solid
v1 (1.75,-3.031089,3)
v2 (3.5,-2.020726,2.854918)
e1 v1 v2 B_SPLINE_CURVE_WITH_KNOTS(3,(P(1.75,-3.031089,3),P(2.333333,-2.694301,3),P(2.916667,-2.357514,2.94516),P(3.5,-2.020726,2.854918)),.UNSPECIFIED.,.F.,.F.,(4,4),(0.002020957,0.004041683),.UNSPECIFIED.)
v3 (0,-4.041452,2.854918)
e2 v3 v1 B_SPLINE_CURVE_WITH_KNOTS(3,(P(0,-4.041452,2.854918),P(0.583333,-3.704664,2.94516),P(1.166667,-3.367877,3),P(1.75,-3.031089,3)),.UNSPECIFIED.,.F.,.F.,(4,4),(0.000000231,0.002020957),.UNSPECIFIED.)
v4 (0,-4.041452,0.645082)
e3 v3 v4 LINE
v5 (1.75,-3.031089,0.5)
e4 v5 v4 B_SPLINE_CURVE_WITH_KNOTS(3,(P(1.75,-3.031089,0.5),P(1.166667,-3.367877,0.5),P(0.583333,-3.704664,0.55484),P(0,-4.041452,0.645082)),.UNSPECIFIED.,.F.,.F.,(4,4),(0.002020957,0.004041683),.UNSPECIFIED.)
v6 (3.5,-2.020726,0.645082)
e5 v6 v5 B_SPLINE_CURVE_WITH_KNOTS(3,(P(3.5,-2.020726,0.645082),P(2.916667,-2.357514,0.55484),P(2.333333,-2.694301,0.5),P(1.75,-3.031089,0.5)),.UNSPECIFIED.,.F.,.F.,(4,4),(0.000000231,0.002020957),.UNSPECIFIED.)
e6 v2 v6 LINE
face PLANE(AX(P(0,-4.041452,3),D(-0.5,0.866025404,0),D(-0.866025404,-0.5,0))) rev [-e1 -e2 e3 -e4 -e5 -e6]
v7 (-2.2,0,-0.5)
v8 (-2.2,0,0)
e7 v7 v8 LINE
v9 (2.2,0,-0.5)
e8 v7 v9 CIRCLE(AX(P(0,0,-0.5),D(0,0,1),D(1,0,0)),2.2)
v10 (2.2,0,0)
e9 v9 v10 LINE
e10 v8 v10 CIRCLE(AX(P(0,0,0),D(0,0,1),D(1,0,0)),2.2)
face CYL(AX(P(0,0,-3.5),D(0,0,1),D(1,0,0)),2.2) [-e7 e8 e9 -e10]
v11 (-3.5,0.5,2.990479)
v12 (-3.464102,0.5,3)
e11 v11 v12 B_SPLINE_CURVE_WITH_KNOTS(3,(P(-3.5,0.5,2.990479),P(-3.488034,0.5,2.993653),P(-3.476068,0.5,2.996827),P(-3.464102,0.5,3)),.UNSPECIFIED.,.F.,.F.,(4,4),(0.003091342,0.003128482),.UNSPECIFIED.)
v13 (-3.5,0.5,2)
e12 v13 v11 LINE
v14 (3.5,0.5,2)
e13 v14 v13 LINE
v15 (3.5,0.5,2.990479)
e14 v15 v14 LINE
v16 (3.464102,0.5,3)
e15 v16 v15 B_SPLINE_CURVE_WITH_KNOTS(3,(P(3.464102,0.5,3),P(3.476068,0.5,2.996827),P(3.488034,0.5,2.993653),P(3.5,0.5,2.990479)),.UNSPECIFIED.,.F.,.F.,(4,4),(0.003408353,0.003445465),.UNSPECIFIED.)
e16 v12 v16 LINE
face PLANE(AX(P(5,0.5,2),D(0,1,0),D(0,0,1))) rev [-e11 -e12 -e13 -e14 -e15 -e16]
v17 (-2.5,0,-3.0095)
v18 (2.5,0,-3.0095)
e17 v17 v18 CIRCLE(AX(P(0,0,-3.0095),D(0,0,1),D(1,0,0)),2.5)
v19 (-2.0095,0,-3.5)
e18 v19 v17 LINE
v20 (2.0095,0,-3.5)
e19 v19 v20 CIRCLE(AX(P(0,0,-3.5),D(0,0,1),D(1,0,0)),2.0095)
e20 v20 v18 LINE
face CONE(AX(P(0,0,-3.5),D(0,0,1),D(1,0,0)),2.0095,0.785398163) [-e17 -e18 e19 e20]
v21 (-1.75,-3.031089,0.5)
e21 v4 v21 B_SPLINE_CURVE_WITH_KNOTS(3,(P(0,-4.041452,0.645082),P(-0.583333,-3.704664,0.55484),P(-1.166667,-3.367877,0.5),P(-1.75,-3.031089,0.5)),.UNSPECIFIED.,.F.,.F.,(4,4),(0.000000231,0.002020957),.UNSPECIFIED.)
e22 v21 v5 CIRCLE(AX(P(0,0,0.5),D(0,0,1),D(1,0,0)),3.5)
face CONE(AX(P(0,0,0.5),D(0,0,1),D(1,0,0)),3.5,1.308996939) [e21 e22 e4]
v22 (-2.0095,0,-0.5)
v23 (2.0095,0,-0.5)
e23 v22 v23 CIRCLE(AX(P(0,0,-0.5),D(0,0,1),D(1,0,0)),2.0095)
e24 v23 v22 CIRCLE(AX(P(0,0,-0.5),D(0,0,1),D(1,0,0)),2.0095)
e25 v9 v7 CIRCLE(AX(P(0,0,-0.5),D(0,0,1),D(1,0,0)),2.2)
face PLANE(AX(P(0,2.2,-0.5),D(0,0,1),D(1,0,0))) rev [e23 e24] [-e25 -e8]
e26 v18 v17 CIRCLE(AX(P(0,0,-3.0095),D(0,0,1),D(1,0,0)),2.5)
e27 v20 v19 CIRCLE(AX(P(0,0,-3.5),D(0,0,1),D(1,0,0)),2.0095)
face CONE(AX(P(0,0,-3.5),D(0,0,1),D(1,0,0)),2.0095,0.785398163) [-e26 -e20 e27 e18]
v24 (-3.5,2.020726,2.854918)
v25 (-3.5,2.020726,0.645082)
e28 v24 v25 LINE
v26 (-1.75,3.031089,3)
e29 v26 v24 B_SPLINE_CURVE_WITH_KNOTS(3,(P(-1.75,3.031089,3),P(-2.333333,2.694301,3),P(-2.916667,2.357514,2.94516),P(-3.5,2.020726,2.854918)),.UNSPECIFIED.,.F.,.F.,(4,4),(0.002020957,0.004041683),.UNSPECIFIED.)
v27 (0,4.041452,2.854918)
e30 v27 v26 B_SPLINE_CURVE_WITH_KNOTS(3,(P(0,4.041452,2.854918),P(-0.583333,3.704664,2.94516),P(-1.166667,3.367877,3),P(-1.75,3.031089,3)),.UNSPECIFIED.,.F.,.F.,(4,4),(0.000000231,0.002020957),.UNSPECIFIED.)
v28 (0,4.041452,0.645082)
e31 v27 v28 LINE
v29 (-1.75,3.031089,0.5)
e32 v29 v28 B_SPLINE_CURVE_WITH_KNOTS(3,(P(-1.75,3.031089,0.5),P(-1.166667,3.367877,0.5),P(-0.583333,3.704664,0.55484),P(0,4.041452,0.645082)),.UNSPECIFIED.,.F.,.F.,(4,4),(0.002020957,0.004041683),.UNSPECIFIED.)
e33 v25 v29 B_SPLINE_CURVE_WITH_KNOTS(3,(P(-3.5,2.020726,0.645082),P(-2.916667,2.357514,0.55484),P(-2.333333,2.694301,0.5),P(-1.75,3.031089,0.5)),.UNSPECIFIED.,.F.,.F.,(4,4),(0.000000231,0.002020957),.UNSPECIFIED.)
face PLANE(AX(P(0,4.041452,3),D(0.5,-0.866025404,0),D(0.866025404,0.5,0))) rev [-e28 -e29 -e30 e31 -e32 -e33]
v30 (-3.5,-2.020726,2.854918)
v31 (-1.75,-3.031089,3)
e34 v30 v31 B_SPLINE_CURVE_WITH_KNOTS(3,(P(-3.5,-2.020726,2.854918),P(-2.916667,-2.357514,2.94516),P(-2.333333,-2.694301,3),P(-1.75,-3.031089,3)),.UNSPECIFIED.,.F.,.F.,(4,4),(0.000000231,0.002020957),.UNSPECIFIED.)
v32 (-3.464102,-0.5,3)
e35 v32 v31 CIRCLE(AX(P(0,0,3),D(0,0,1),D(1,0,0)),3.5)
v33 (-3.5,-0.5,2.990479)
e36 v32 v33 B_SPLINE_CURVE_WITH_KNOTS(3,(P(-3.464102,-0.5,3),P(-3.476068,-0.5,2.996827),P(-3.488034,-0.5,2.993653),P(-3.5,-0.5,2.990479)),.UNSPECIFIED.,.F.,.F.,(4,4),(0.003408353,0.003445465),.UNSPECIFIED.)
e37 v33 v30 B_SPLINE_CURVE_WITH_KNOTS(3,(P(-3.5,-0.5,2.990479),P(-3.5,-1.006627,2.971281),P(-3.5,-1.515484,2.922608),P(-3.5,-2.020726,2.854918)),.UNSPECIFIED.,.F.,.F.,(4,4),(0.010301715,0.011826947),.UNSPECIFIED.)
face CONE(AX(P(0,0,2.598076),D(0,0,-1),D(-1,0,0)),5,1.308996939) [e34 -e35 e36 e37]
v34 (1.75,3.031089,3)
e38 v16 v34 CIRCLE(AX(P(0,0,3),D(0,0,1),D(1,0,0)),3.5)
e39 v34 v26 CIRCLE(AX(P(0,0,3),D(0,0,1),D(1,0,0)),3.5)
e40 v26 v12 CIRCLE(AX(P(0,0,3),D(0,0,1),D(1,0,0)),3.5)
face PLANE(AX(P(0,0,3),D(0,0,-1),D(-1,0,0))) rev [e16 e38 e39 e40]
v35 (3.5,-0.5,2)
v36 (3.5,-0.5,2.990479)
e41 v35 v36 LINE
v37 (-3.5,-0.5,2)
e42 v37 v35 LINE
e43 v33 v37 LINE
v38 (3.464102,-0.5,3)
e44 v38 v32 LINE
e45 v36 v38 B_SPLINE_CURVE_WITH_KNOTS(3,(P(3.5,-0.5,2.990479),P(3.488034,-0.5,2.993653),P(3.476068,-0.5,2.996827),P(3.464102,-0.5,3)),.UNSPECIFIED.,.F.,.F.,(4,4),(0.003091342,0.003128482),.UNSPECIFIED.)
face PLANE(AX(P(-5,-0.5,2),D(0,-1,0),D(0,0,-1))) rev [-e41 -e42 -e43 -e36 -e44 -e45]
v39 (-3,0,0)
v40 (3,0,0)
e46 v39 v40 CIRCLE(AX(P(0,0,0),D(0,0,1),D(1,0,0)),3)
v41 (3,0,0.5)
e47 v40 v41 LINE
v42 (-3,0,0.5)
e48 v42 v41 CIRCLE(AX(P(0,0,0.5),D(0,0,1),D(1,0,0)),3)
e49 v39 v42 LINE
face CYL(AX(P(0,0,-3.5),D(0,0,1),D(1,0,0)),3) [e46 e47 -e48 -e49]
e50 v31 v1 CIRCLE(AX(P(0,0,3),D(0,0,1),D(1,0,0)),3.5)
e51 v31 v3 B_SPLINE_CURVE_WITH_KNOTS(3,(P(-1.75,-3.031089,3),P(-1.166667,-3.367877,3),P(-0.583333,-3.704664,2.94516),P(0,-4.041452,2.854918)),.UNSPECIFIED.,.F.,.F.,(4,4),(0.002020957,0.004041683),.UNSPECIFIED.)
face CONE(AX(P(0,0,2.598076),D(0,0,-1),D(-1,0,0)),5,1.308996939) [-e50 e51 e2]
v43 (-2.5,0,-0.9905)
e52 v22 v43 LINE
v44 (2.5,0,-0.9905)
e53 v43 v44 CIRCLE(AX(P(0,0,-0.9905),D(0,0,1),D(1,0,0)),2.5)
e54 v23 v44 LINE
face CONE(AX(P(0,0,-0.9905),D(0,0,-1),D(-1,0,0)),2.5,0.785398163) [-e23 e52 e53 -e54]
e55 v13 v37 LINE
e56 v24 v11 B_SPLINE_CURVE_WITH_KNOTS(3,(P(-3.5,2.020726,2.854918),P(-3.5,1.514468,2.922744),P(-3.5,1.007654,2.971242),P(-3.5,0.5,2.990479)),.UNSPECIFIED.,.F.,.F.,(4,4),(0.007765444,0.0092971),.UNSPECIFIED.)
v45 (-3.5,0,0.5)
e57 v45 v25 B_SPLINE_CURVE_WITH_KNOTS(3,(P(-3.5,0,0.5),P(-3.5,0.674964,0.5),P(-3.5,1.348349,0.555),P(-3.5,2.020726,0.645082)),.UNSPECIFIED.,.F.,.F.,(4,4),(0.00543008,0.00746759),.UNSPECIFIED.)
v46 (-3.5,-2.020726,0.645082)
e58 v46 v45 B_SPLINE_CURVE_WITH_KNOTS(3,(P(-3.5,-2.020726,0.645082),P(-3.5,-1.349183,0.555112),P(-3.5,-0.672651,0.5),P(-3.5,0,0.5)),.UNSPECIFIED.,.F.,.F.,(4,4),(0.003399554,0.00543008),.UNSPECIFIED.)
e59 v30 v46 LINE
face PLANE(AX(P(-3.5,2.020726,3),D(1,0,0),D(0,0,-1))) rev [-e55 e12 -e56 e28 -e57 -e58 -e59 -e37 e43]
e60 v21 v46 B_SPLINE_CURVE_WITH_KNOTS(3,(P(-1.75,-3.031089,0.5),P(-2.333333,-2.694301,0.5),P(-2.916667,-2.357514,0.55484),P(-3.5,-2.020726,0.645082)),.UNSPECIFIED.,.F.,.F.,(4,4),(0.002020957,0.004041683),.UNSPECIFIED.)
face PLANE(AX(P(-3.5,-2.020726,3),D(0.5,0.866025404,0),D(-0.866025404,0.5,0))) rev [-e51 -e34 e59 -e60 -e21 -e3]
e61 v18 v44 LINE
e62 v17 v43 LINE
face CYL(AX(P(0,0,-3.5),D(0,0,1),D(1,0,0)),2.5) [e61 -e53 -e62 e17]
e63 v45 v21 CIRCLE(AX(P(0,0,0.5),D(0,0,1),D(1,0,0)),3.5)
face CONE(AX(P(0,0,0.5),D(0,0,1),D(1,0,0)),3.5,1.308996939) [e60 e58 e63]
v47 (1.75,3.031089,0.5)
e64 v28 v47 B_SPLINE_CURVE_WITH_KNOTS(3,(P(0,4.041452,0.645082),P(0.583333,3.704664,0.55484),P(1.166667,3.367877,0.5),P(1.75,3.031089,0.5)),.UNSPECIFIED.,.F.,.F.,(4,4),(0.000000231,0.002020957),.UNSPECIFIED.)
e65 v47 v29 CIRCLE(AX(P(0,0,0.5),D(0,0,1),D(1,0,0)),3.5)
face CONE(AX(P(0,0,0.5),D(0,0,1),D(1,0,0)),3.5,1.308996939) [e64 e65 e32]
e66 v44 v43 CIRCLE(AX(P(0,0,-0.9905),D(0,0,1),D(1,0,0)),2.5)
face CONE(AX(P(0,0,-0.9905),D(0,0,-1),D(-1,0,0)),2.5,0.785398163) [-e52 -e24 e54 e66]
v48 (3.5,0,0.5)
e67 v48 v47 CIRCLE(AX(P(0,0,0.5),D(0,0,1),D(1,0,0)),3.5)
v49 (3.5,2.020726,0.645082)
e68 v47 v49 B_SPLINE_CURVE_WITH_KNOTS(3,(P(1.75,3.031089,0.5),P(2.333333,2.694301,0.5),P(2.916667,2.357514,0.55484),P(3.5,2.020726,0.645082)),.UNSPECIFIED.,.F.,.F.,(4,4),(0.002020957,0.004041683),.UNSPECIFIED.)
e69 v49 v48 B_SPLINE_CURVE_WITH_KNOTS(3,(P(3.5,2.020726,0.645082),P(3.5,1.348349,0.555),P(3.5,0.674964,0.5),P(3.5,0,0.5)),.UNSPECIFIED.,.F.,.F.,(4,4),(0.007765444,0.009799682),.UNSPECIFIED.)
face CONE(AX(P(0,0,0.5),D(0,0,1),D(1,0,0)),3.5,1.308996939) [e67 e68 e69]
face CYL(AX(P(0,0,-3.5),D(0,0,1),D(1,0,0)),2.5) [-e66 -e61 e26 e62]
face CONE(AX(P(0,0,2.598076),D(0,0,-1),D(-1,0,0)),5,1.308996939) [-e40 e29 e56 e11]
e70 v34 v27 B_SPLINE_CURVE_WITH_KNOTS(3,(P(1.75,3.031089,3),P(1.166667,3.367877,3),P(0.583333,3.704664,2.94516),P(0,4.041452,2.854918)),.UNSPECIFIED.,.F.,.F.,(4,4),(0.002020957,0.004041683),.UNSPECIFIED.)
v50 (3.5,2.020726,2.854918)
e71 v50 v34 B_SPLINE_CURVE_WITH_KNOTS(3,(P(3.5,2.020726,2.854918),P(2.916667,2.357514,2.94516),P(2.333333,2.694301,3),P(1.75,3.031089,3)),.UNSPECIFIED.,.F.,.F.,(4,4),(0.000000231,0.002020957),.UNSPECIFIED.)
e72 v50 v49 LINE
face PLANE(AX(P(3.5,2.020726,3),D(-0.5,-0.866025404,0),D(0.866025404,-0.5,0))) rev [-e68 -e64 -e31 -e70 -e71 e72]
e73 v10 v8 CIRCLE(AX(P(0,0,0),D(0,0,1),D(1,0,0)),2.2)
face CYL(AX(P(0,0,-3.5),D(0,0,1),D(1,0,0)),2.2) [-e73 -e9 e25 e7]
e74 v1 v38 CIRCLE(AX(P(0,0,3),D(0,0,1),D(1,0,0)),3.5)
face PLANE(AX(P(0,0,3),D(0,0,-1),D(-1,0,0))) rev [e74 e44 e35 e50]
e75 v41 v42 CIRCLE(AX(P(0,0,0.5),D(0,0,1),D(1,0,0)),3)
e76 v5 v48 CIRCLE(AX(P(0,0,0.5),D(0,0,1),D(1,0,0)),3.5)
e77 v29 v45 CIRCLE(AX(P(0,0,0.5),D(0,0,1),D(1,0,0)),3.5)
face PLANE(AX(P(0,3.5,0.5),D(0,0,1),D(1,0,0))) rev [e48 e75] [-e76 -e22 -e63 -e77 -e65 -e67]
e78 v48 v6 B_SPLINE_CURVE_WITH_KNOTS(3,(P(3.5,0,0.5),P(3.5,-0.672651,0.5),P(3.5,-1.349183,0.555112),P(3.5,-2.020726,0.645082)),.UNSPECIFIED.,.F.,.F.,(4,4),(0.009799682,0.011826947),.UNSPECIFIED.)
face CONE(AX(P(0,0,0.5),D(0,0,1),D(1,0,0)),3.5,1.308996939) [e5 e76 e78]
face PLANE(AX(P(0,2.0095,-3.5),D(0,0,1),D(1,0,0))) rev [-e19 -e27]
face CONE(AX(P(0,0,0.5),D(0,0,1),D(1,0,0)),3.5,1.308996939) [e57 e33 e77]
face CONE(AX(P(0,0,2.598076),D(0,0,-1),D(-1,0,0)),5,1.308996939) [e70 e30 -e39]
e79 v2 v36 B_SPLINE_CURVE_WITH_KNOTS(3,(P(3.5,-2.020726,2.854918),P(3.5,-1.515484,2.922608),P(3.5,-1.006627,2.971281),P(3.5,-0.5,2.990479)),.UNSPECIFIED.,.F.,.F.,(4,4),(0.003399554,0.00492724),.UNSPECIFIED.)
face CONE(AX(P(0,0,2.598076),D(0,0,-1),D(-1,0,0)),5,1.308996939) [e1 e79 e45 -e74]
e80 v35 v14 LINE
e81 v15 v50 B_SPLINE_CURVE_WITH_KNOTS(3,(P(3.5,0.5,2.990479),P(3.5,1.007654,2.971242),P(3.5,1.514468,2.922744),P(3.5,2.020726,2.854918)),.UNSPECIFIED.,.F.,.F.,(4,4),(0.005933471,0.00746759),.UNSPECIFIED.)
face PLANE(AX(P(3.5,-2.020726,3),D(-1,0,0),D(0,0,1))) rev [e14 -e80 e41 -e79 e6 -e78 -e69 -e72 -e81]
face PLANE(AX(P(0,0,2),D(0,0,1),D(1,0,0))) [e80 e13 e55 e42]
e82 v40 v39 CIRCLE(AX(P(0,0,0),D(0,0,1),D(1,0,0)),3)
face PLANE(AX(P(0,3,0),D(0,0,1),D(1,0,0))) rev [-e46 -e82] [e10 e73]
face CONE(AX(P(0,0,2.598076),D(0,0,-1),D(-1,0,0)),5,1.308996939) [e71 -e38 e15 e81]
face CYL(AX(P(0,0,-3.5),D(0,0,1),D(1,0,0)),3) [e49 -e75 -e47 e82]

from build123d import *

# Parameters (mm, degrees)
SKETCH_2_R          = 5
CUT_EXTRUDE_1_DEPTH = 3
SKETCH_3_W          = 10
SKETCH_3_H          = 1
CUT_EXTRUDE_2_DEPTH = 1


with BuildPart() as part:
    # 草图1 → 旋转1 (revolve)
    with BuildSketch(Plane(origin=(0, 0, 0), x_dir=(0, 0, -1), z_dir=(1, 0, 0)), mode=Mode.PRIVATE) as revolve_1_sk:
        Polygon((-3, 0), (-3, 3.5), (-2.598076211, 5), (-0.901923789, 5), (-0.5, 3.5), (-0.5, 3), (0, 3), (0, 2.2), (0.5, 2.2), (0.5, 2.0095), (0.9905, 2.5), (3.0095, 2.5), (3.5, 2.0095), (3.5, 0), align=None)
    revolve(revolve_1_sk.sketch.rotate(Axis((0, 0, -3.5), (0, 0, 1)), 270), axis=Axis((0, 0, -3.5), (0, 0, 1)))

    # 草图2 → 切除-拉伸1 (cut)
    with BuildSketch(Plane.XY):
        Circle(SKETCH_2_R)
        Polygon((-3.5, 2.020725942), (-3.5, -2.020725942), (0, -4.041451884), (3.5, -2.020725942), (3.5, 2.020725942), (0, 4.041451884), align=None, mode=Mode.SUBTRACT)
    extrude(amount=CUT_EXTRUDE_1_DEPTH, mode=Mode.SUBTRACT)

    # 草图3 → 切除-拉伸2 (cut)
    with BuildSketch(Plane.XY.offset(3)):
        Rectangle(SKETCH_3_W, SKETCH_3_H)
    extrude(amount=-CUT_EXTRUDE_2_DEPTH, mode=Mode.SUBTRACT)


solid = part.part
